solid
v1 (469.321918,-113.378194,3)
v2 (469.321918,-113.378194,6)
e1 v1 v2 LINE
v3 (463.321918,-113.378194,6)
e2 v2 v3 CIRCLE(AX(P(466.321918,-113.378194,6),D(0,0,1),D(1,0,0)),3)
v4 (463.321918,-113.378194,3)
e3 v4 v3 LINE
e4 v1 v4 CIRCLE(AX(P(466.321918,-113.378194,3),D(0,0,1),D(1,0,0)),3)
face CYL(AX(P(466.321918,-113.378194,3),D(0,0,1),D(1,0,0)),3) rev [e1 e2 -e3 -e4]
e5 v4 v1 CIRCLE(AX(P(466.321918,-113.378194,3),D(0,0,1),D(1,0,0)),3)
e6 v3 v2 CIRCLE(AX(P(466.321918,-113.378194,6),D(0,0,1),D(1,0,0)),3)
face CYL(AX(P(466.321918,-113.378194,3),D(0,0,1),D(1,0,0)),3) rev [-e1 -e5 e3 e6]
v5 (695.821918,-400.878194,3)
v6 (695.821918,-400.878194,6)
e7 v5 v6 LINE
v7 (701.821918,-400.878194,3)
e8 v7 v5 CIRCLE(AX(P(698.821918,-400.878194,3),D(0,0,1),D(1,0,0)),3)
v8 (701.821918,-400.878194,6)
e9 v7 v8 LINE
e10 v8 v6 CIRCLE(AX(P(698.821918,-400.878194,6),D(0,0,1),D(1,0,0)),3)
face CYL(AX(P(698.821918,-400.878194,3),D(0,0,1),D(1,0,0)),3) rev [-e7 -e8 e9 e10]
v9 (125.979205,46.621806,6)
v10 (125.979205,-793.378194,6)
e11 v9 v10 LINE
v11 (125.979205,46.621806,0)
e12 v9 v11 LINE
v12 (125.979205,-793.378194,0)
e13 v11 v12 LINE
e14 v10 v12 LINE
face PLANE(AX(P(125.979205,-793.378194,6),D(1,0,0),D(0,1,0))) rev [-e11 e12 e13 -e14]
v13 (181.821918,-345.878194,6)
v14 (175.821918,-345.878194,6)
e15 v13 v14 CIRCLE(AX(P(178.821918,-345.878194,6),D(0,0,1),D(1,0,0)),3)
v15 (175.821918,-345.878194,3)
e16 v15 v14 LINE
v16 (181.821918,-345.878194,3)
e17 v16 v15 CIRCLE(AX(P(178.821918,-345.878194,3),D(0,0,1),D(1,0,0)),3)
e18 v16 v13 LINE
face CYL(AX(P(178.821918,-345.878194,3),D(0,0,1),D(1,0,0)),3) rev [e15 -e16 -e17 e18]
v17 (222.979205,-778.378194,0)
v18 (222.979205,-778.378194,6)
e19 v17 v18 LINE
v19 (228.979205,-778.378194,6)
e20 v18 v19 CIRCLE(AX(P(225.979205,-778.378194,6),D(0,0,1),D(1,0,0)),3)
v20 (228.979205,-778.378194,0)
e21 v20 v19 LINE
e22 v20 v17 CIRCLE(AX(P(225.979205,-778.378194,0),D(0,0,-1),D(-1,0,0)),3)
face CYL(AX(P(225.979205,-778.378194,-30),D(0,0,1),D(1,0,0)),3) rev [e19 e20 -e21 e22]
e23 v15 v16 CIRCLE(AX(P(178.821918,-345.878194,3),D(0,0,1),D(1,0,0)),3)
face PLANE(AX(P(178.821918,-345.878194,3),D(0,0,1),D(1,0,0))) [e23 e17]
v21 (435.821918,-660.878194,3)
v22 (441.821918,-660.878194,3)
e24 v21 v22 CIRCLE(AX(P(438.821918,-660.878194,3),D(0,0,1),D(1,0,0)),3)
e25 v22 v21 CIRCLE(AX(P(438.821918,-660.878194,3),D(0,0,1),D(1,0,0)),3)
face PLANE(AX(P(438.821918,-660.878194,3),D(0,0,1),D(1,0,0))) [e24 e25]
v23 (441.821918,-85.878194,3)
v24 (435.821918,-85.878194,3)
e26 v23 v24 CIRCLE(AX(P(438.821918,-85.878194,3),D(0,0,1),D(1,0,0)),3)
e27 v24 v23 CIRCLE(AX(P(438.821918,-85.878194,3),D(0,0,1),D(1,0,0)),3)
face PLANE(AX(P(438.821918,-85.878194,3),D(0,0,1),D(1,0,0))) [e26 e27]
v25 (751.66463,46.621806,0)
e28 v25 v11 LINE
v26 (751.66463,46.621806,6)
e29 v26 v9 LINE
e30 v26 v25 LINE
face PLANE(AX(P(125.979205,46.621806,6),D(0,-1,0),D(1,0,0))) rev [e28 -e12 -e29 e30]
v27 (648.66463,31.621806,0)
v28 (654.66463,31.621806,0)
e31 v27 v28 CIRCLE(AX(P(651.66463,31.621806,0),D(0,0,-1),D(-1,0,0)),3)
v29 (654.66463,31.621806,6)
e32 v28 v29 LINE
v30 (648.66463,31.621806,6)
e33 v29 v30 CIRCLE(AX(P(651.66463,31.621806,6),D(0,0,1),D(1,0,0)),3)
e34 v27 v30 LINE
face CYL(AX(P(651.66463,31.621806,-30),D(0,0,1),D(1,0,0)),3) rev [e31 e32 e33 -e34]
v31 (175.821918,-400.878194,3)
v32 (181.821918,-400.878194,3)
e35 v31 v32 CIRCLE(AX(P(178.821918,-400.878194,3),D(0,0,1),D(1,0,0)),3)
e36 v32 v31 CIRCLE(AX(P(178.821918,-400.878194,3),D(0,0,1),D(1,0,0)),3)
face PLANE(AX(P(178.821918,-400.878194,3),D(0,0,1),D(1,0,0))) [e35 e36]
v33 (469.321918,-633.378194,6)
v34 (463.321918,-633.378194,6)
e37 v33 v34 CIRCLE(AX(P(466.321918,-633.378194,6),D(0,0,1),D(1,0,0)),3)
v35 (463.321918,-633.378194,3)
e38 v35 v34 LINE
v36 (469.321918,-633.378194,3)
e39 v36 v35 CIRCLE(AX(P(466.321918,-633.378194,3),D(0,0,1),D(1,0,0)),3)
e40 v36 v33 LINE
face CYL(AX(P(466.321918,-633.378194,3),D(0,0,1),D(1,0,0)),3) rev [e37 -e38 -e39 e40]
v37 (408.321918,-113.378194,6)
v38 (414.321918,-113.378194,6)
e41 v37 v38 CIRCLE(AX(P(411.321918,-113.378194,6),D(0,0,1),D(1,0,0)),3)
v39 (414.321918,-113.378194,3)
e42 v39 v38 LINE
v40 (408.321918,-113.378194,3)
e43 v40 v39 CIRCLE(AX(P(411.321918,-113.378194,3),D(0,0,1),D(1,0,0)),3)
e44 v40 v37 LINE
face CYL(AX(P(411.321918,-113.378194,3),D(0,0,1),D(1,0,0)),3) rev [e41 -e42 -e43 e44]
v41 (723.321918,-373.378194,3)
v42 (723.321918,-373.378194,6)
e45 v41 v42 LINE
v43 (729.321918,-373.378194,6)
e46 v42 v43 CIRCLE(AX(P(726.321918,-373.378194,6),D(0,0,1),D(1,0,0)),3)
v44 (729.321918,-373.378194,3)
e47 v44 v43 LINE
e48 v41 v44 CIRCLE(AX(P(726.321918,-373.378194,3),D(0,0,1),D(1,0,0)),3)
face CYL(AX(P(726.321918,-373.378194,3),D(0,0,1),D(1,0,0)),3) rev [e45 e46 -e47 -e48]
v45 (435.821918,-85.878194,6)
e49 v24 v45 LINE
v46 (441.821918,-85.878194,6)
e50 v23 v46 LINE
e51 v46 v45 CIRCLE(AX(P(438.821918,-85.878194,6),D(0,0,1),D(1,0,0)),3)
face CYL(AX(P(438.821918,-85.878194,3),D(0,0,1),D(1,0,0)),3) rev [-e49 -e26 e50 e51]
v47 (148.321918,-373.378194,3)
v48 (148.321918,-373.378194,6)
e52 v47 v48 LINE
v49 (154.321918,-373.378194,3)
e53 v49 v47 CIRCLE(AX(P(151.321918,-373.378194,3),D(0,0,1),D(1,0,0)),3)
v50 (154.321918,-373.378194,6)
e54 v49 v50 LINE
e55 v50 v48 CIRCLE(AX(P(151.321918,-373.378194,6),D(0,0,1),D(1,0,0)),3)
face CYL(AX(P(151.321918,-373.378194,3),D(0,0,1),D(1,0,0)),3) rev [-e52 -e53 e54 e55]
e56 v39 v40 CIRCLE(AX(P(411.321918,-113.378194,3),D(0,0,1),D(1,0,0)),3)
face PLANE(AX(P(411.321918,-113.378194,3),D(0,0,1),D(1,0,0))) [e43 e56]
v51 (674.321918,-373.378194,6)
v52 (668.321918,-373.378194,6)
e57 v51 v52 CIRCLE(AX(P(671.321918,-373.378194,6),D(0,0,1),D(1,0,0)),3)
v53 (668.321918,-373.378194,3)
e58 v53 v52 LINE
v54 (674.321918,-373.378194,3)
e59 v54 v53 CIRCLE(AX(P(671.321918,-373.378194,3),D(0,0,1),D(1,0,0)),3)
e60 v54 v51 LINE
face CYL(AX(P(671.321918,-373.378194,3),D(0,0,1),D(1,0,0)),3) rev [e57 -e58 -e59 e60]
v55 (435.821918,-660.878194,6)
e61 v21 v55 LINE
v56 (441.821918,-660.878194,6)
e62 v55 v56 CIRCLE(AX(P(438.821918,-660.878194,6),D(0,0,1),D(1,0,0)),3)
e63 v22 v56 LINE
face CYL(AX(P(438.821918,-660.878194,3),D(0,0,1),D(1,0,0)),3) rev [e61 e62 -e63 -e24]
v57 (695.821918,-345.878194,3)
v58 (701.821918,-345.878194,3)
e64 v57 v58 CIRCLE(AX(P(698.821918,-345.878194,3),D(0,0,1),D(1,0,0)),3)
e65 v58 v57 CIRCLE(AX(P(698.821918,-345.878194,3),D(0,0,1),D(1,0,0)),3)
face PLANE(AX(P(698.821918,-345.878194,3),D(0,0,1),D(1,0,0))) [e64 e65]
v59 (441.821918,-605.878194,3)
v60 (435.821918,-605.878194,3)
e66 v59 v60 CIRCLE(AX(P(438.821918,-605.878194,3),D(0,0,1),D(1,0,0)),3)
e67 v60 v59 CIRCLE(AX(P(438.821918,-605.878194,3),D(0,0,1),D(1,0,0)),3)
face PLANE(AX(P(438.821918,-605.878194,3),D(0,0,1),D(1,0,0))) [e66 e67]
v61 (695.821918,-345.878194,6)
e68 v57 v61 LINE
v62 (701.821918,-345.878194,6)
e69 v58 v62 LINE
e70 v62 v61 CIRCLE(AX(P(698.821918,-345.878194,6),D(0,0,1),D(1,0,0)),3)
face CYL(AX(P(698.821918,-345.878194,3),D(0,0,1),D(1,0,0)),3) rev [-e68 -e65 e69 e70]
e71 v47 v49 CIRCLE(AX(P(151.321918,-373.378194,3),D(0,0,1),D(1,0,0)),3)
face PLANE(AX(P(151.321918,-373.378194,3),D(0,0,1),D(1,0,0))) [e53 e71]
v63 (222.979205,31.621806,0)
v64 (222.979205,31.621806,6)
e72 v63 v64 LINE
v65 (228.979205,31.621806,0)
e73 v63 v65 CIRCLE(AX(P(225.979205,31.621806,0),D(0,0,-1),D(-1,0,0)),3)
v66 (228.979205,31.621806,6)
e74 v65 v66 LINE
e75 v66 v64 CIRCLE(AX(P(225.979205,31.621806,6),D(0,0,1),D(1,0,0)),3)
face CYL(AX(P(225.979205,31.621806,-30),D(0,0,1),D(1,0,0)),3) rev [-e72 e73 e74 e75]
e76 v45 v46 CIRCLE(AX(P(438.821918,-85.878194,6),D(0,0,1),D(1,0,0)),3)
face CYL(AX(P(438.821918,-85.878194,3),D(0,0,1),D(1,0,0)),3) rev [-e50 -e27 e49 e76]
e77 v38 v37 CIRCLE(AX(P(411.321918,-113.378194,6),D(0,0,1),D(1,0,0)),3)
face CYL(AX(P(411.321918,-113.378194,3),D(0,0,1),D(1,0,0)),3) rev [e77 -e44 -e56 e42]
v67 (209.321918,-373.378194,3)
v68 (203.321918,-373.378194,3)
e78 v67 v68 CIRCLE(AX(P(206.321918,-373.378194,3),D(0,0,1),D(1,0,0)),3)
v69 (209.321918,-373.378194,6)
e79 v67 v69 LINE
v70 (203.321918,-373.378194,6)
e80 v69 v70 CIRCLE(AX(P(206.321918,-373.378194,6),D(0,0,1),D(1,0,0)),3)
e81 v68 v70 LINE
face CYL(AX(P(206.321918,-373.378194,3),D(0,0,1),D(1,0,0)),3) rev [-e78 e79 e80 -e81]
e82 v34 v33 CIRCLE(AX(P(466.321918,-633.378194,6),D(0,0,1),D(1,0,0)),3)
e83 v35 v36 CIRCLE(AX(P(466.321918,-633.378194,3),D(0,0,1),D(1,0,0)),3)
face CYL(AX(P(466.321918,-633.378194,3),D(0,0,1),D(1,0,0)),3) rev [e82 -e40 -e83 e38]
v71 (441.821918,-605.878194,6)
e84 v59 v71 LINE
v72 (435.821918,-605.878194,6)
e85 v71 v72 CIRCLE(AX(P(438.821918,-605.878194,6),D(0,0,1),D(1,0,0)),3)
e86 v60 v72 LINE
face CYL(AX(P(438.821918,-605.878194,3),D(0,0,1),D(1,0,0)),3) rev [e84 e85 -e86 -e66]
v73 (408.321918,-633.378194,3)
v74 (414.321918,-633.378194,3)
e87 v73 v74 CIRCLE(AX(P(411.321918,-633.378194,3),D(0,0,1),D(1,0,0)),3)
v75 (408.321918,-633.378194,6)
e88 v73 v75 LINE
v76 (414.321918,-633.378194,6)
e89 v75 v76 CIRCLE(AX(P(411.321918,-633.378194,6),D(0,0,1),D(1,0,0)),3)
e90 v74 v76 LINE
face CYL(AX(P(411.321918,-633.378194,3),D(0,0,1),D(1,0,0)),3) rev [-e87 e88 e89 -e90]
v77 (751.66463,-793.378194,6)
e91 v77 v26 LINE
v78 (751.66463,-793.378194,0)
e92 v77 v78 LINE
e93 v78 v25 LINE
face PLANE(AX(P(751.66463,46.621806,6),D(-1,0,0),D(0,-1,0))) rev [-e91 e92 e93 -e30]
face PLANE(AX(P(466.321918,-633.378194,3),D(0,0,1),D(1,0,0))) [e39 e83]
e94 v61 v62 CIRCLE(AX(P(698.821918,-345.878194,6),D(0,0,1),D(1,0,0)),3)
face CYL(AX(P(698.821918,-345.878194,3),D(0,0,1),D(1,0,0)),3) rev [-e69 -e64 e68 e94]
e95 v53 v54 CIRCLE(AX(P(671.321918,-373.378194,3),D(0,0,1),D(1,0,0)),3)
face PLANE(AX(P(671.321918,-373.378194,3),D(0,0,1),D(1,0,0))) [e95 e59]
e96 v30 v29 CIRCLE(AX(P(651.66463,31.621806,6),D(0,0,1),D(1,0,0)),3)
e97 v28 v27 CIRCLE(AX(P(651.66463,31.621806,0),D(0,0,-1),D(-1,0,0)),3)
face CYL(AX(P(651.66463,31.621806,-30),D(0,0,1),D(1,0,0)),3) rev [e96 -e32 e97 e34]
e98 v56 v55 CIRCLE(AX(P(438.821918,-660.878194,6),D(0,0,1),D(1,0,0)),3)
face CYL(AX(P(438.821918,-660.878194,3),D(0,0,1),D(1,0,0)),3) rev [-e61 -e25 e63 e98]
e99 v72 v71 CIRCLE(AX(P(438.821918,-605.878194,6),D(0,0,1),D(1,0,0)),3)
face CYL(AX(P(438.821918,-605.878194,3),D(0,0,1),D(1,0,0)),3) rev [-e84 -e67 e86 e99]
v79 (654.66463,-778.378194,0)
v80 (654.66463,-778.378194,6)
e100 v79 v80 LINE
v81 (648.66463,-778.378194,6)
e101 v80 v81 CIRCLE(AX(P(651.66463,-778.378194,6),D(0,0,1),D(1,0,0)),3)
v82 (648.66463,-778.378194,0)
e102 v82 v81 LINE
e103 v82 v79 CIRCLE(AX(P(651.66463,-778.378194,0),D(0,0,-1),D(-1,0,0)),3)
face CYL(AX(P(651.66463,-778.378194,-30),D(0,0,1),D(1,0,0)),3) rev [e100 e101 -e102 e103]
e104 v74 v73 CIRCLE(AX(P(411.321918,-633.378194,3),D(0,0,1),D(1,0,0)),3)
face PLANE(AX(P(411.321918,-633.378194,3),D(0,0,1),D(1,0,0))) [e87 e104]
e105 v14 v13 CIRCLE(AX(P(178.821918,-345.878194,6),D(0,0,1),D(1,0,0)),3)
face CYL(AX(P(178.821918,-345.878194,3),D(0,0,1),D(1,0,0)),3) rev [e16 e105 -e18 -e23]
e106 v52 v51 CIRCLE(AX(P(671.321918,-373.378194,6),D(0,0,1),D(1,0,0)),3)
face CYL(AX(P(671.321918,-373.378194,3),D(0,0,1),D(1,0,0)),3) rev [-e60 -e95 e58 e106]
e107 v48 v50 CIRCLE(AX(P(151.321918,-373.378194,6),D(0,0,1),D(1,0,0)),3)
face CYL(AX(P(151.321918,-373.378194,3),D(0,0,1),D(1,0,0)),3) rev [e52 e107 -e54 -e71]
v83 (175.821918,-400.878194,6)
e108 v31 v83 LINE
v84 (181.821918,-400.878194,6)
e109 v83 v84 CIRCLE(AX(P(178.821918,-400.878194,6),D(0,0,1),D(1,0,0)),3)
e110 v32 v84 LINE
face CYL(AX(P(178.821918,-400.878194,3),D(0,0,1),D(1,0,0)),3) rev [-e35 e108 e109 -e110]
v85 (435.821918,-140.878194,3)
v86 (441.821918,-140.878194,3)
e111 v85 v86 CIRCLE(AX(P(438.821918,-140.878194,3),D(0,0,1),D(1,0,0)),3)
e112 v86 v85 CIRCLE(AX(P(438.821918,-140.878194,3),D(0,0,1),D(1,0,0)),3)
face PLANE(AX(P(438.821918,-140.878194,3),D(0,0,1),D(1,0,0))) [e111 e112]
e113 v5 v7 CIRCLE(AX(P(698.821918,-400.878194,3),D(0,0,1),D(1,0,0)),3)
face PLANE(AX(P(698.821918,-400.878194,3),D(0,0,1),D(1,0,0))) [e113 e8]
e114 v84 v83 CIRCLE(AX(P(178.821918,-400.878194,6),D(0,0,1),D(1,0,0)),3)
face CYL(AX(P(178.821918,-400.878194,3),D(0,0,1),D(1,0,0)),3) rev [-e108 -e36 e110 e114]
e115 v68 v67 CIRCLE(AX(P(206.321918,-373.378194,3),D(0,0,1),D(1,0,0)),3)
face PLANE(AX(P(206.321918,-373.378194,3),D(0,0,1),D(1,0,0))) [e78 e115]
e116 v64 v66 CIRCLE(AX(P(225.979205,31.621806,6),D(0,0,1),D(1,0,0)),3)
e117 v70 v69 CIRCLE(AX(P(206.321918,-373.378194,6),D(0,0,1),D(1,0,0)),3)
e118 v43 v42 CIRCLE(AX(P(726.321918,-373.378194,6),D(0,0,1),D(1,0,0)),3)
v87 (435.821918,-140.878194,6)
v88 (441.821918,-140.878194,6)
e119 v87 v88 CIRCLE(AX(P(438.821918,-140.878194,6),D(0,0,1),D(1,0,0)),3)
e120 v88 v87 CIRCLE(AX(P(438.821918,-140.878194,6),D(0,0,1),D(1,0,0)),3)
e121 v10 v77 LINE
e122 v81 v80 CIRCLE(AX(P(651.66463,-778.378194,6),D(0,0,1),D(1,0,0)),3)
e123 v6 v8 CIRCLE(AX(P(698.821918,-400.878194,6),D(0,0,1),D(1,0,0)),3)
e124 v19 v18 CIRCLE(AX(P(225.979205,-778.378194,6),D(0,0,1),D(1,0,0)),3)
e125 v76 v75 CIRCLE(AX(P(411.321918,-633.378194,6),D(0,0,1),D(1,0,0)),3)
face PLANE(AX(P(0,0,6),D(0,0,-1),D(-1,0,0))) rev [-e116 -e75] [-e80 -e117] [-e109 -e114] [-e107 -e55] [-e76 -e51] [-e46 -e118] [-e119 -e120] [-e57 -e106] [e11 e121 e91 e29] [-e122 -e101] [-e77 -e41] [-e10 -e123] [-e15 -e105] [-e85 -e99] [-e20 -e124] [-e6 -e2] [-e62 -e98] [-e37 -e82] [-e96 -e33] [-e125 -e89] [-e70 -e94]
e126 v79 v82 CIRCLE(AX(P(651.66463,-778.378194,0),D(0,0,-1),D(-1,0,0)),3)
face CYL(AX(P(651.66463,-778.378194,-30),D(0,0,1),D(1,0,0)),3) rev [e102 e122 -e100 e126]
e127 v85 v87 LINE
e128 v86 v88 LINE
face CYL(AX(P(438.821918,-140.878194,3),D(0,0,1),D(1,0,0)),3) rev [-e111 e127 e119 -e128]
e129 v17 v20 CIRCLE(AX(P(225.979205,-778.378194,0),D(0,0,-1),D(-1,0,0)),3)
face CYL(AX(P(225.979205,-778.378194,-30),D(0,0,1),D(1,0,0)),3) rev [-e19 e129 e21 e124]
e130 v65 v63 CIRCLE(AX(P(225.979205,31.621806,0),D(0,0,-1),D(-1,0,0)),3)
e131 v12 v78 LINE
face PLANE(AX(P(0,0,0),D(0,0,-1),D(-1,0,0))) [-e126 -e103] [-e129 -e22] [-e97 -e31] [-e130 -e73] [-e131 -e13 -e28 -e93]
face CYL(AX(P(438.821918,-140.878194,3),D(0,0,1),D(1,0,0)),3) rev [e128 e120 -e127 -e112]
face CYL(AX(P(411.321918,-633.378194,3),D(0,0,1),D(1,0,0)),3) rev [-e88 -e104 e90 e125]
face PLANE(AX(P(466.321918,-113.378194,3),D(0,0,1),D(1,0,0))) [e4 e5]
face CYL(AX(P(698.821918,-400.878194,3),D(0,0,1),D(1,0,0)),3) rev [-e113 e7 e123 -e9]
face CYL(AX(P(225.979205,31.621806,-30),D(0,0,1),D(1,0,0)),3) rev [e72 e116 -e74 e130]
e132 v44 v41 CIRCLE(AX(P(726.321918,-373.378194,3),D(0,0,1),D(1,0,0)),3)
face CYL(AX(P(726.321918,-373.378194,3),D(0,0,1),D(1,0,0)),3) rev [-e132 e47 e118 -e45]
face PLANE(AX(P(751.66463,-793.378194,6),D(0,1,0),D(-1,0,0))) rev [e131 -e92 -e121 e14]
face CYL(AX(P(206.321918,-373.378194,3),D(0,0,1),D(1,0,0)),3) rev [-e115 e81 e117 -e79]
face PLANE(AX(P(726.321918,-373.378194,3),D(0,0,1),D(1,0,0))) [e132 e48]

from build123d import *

# Parameters (mm, degrees)
SKETCH2_W           = 625.68542495
SKETCH2_H           = 840
BOSS_EXTRUDE1_DEPTH = 6
SKETCH3_R           = 3
CUT_EXTRUDE1_DEPTH  = 3
CUT_EXTRUDE2_DEPTH  = 36


with BuildPart() as part:
    # Sketch2 → Boss-Extrude1 (new body)
    with BuildSketch(Plane.XY):
        with Locations((438.821917673, -373.378193942)):
            Rectangle(SKETCH2_W, SKETCH2_H)
    extrude(amount=BOSS_EXTRUDE1_DEPTH)

    # Sketch3 → Cut-Extrude1 (cut)
    with BuildSketch(Plane.XY.offset(6)):
        with Locations((438.821917673, -660.878193942)):
            Circle(SKETCH3_R)
        with Locations((411.321917673, -633.378193942)):
            Circle(SKETCH3_R)
        with Locations((438.821917673, -605.878193942)):
            Circle(SKETCH3_R)
        with Locations((466.321917673, -633.378193942)):
            Circle(SKETCH3_R)
        with Locations((151.321917673, -373.378193942)):
            Circle(SKETCH3_R)
        with Locations((178.821917673, -345.878193942)):
            Circle(SKETCH3_R)
        with Locations((206.321917673, -373.378193942)):
            Circle(SKETCH3_R)
        with Locations((178.821917673, -400.878193942)):
            Circle(SKETCH3_R)
        with Locations((438.821917673, -140.878193942)):
            Circle(SKETCH3_R)
        with Locations((411.321917673, -113.378193942)):
            Circle(SKETCH3_R)
        with Locations((438.821917673, -85.878193942)):
            Circle(SKETCH3_R)
        with Locations((466.321917673, -113.378193942)):
            Circle(SKETCH3_R)
        with Locations((698.821917673, -400.878193942)):
            Circle(SKETCH3_R)
        with Locations((671.321917673, -373.378193942)):
            Circle(SKETCH3_R)
        with Locations((698.821917673, -345.878193942)):
            Circle(SKETCH3_R)
        with Locations((726.321917673, -373.378193942)):
            Circle(SKETCH3_R)
    extrude(amount=-CUT_EXTRUDE1_DEPTH, mode=Mode.SUBTRACT)

    # Sketch6 → Cut-Extrude2 (cut)
    with BuildSketch(Plane.XY.offset(6)):
        with BuildLine():
            ThreePointArc((654.664630148, -778.378193942), (651.664630148, -775.378193942), (648.664630148, -778.378193942))
            Line((648.664630148, -778.378193942), (654.664630148, -778.378193942))
        make_face()
        with BuildLine():
            Line((654.664630148, -778.378193942), (648.664630148, -778.378193942))
            ThreePointArc((648.664630148, -778.378193942), (651.664630148, -781.378193942), (654.664630148, -778.378193942))
        make_face()
        with BuildLine():
            ThreePointArc((228.979205198, -778.378193942), (225.979205198, -775.378193942), (222.979205198, -778.378193942))
            Line((222.979205198, -778.378193942), (228.979205198, -778.378193942))
        make_face()
        with BuildLine():
            Line((228.979205198, -778.378193942), (222.979205198, -778.378193942))
            ThreePointArc((222.979205198, -778.378193942), (225.979205198, -781.378193942), (228.979205198, -778.378193942))
        make_face()
        with BuildLine():
            ThreePointArc((222.979205198, 31.621806058), (225.979205198, 28.621806058), (228.979205198, 31.621806058))
            Line((228.979205198, 31.621806058), (222.979205198, 31.621806058))
        make_face()
        with BuildLine():
            Line((222.979205198, 31.621806058), (228.979205198, 31.621806058))
            ThreePointArc((228.979205198, 31.621806058), (225.979205198, 34.621806058), (222.979205198, 31.621806058))
        make_face()
        with BuildLine():
            Line((648.664630148, 31.621806058), (651.664630148, 31.621806058))
            Line((651.664630148, 31.621806058), (654.664630148, 31.621806058))
            ThreePointArc((654.664630148, 31.621806058), (651.664630148, 34.621806058), (648.664630148, 31.621806058))
        make_face()
        with BuildLine():
            Line((654.664630148, 31.621806058), (651.664630148, 31.621806058))
            Line((651.664630148, 31.621806058), (648.664630148, 31.621806058))
            ThreePointArc((648.664630148, 31.621806058), (651.664630148, 28.621806058), (654.664630148, 31.621806058))
        make_face()
    extrude(amount=-CUT_EXTRUDE2_DEPTH, mode=Mode.SUBTRACT)


solid = part.part
